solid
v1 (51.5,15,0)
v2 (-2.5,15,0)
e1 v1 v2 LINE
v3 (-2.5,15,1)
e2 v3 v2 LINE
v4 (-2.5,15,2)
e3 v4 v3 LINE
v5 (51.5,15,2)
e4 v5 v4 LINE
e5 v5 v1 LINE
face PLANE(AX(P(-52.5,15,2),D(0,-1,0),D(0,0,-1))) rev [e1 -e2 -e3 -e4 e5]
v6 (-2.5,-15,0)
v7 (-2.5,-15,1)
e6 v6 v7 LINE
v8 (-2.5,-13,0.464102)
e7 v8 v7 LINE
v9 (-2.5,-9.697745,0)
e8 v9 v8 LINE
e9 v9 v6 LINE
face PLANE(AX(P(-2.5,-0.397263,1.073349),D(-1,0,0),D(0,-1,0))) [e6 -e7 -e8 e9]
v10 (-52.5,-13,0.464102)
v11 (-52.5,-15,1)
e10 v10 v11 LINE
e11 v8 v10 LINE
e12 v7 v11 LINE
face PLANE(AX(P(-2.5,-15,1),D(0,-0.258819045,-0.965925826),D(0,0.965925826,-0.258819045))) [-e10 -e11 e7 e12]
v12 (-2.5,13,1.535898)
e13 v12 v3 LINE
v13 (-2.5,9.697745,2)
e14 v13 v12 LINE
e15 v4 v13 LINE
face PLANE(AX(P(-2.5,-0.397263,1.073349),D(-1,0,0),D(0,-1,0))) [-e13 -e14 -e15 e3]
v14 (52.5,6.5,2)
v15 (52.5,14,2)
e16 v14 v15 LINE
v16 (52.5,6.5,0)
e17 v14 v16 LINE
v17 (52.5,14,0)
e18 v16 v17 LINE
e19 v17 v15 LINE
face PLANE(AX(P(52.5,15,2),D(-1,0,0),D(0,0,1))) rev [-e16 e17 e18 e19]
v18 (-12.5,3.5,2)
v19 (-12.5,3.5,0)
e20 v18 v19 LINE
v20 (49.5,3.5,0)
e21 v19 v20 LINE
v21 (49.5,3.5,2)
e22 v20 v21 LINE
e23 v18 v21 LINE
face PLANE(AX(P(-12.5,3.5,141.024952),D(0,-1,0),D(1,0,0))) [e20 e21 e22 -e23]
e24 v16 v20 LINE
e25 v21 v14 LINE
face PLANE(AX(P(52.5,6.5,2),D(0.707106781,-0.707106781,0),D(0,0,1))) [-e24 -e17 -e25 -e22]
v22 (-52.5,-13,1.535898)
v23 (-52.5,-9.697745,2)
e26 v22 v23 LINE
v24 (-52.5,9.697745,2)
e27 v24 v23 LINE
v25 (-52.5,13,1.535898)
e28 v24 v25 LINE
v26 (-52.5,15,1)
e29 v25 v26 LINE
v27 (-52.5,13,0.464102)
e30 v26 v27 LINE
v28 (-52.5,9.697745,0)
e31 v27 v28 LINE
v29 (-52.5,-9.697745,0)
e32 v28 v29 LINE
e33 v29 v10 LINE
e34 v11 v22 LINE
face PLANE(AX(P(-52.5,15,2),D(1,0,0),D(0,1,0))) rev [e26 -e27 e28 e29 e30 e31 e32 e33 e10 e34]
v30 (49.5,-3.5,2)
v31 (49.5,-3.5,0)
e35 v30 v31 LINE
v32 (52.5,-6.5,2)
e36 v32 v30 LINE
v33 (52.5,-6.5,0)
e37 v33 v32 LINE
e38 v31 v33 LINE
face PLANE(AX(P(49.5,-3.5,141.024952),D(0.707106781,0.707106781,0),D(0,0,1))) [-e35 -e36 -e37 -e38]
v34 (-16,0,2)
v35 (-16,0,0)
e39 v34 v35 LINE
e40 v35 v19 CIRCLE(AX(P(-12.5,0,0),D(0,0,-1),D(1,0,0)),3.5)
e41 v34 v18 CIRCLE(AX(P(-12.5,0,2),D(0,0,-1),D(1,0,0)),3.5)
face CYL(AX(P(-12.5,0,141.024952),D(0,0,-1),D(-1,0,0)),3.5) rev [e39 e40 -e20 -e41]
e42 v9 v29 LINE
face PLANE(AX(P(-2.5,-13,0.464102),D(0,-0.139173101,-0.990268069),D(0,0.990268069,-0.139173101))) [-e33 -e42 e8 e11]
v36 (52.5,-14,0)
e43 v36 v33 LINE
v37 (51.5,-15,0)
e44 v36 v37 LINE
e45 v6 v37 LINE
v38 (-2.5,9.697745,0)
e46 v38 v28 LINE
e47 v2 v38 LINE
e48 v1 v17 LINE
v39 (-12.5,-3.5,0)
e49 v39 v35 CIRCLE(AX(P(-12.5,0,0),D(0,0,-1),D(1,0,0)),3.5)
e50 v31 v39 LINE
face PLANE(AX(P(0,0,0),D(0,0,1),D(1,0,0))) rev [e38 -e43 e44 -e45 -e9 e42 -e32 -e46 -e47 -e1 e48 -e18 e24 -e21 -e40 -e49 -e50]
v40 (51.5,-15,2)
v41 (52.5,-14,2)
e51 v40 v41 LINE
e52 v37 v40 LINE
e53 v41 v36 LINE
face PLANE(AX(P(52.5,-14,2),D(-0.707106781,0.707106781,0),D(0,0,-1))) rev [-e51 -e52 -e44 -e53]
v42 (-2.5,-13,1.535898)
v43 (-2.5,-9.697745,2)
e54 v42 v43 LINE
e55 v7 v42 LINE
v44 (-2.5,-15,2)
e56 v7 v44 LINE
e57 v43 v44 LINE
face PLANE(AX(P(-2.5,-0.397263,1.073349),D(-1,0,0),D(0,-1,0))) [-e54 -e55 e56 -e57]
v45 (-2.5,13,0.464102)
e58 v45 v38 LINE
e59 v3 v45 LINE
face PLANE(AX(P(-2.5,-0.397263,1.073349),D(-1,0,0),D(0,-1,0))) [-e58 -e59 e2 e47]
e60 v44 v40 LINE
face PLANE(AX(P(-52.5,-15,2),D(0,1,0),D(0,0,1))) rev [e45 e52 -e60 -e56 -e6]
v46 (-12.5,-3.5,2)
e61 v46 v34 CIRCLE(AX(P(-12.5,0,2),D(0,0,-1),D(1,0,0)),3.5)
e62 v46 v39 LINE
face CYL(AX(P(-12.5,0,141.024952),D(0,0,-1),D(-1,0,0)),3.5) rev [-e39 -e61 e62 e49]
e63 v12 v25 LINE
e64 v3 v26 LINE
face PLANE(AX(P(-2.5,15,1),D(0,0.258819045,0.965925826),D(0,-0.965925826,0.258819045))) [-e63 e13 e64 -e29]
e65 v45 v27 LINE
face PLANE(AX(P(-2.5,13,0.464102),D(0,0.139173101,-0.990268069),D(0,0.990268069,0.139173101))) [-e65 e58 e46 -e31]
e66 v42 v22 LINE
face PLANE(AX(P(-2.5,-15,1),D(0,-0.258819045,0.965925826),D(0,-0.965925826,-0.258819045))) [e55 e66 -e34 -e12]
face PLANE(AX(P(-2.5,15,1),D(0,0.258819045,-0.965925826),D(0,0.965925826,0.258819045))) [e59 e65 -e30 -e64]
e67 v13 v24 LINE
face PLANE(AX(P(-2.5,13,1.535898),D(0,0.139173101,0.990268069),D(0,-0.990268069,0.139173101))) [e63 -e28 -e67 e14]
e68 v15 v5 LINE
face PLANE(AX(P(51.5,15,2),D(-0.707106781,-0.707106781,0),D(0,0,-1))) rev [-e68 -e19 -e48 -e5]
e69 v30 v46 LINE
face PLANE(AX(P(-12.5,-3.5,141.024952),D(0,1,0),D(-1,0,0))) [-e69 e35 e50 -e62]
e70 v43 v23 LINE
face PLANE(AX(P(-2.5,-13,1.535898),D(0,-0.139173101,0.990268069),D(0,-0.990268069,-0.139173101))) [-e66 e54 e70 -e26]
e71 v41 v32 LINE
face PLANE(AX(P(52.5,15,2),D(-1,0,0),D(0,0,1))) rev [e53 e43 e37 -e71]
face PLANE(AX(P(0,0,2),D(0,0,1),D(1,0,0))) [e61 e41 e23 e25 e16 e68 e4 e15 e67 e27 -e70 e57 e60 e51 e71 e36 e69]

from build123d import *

# Parameters (mm, degrees)
SKETCH_2_W               = 105
SKETCH_2_H               = 30
EXTRUDE_1_DEPTH          = 2
CUT_EXTRUDE_1_DEPTH      = 55.637441375
CUT_EXTRUDE_1_DEPTH_BACK = 55.637441375
SKETCH_5_OUTSIDE_W       = 25.844
SKETCH_5_OUTSIDE_H       = 53.844
CUT_EXTRUDE_7_DEPTH      = 50
CHAMFER_1_SIZE           = 1
CHAMFER_2_SIZE           = 3


with BuildPart() as part:
    # 草图2 → 凸台-拉伸1 (new body)
    with BuildSketch(Plane.XY):
        Rectangle(SKETCH_2_W, SKETCH_2_H)
    extrude(amount=EXTRUDE_1_DEPTH)

    # 草图3 → 切除-拉伸1 (cut, two sides: drawn at the far end of the back side and taken through both)
    with BuildSketch(Plane.XY.offset(2).offset(-CUT_EXTRUDE_1_DEPTH_BACK)):
        with BuildLine():
            Line((52.5, 3.5), (-12.5, 3.5))
            ThreePointArc((-12.5, 3.5), (-16, 0), (-12.5, -3.5))
            Line((-12.5, -3.5), (52.5, -3.5))
            Line((52.5, -3.5), (52.5, 3.5))
        make_face()
    extrude(amount=CUT_EXTRUDE_1_DEPTH + CUT_EXTRUDE_1_DEPTH_BACK, mode=Mode.SUBTRACT)

    # 草图5 outside → 切除-拉伸7 (cut)
    with BuildSketch(Plane.ZY.offset(52.5)):
        with Locations((1, 0)):
            Rectangle(SKETCH_5_OUTSIDE_W, SKETCH_5_OUTSIDE_H)
        Polygon((1, 15), (0.464101615, 13), (0, 9.69774542), (0, -9.69774542), (0.464101615, -13), (1, -15), (1.535898385, -13), (2, -9.69774542), (2, 9.69774542), (1.535898385, 13), align=None, mode=Mode.SUBTRACT)
    extrude(amount=-CUT_EXTRUDE_7_DEPTH, mode=Mode.SUBTRACT)

    # 倒角1
    chamfer_1_edges = [part.edges().sort_by_distance(p)[0] for p in [
        (52.5, -15, 1),
        (52.5, 15, 1),
    ]]
    chamfer(chamfer_1_edges, length=CHAMFER_1_SIZE)

    # 倒角2
    chamfer_2_edges = [part.edges().sort_by_distance(p)[0] for p in [
        (52.5, -3.5, 1),
        (52.5, 3.5, 1),
    ]]
    chamfer(chamfer_2_edges, length=CHAMFER_2_SIZE)


solid = part.part
